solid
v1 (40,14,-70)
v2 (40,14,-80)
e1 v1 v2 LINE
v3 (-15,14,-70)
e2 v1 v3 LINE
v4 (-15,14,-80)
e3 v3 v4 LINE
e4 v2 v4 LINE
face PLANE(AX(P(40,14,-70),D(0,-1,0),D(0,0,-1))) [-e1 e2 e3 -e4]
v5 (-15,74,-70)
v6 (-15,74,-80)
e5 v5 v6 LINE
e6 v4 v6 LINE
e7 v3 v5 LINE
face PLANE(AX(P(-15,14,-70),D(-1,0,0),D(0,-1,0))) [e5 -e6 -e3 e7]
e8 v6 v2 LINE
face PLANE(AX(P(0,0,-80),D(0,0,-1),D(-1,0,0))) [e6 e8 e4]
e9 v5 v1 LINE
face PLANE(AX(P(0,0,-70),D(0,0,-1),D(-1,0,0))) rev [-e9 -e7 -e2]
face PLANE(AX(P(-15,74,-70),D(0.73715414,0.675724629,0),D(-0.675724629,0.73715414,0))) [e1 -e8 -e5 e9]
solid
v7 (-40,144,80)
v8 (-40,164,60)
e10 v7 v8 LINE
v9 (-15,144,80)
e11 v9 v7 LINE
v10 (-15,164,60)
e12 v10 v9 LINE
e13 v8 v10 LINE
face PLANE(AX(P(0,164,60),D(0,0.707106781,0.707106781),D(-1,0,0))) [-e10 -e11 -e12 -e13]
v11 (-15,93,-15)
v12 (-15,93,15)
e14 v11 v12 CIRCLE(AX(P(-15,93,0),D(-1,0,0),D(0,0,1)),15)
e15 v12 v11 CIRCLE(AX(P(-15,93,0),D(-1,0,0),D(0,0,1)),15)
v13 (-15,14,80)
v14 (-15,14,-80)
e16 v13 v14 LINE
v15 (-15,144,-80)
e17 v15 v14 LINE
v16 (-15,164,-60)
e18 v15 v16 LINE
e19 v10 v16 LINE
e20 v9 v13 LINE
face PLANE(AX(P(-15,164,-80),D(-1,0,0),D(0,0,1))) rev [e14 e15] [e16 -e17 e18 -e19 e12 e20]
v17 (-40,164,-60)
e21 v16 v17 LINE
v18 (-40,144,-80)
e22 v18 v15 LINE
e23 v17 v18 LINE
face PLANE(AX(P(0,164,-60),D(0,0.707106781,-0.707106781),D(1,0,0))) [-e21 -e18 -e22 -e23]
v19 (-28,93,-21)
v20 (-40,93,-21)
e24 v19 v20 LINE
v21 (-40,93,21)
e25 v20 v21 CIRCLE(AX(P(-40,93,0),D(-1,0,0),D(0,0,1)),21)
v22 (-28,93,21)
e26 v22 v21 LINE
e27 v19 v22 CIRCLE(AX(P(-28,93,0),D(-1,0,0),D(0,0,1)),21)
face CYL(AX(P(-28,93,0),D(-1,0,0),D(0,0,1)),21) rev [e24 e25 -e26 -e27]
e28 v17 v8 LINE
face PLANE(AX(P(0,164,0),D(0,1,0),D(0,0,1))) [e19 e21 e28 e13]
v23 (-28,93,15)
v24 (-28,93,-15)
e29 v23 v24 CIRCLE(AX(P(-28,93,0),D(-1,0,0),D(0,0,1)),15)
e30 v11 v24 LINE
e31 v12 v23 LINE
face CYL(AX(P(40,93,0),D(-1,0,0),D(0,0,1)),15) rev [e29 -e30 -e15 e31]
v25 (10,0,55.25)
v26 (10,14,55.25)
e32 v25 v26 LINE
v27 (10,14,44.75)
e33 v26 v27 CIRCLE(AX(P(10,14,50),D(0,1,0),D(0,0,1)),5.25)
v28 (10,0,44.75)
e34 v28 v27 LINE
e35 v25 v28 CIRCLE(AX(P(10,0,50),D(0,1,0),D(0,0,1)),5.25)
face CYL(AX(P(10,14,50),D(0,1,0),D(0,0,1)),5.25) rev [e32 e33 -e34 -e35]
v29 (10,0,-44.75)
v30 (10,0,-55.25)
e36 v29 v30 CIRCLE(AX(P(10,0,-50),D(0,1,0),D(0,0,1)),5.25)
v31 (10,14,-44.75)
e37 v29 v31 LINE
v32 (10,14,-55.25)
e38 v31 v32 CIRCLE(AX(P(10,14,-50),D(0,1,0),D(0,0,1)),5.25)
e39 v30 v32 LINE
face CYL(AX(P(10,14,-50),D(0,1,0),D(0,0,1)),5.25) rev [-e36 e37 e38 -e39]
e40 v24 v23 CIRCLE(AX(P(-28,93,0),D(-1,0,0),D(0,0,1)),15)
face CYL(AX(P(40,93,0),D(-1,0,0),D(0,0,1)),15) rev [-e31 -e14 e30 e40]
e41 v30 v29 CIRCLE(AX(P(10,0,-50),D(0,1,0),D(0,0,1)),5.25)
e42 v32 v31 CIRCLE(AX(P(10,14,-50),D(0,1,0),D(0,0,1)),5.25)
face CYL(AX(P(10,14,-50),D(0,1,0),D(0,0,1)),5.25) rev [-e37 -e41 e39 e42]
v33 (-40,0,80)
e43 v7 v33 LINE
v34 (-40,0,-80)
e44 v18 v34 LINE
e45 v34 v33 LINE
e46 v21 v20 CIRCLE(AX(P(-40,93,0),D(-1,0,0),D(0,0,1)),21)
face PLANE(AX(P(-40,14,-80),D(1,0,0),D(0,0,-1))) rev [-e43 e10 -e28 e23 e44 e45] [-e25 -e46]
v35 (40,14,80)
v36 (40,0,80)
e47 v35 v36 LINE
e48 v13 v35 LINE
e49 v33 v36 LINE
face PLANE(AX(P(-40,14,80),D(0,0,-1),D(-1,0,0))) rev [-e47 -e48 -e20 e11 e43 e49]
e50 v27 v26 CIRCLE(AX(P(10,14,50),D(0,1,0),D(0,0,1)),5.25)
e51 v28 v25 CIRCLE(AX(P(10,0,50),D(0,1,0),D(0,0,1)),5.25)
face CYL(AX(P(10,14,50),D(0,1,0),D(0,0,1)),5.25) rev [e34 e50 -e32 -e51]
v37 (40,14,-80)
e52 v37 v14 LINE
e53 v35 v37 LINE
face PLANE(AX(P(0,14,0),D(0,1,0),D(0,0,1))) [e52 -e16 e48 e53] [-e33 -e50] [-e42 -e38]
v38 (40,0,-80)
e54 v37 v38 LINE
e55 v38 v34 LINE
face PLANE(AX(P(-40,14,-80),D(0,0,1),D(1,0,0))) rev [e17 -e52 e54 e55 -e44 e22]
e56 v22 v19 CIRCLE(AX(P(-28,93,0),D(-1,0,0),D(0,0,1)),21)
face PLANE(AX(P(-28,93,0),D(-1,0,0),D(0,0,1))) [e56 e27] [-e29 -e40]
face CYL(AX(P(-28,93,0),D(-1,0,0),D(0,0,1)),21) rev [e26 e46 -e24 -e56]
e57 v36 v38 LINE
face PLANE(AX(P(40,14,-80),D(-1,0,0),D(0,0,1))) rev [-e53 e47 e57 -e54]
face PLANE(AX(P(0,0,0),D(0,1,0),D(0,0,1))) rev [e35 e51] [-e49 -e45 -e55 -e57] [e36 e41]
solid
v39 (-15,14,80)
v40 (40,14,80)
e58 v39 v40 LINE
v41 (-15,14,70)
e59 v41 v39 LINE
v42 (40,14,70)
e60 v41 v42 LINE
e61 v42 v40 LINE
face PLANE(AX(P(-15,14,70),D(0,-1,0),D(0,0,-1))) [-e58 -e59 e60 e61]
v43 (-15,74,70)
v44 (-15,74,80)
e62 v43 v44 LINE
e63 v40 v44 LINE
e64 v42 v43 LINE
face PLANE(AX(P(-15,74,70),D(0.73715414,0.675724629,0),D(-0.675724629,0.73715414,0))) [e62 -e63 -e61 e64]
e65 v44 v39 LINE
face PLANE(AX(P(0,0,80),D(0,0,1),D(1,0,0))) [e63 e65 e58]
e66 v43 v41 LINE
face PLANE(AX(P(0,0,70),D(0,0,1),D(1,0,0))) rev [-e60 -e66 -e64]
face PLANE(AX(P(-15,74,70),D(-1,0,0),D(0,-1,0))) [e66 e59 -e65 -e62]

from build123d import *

# Parameters (mm, degrees)
SKETCH_1_W                         = 80
SKETCH_1_H                         = 160
EXTRUDE_1_DEPTH                    = 14
SKETCH_2_W                         = 25
SKETCH_2_H                         = 160
EXTRUDE_2_DEPTH                    = 150
EXTRUDE_3_DEPTH                    = 10
EXTRUDE_4_DEPTH                    = 10
SKETCH_5_R                         = 21
CUT_EXTRUDE_1_DEPTH                = 12
SKETCH_6_R                         = 15
CUT_EXTRUDE_2_DEPTH                = 195.730583114
HOLE_WIZARD_10_5_10_5_1_AT_2_COUNT = 2
HOLE_WIZARD_10_5_10_5_1_AT_2_PITCH = 100
CHAMFER_1_SIZE                     = 20


with BuildPart() as part:
    # 草图1 → 凸台-拉伸1 (new body)
    with BuildSketch(Plane(origin=(0, 0, 0), x_dir=(1, 0, 0), z_dir=(0, 1, 0))):
        Rectangle(SKETCH_1_W, SKETCH_1_H)
    extrude(amount=EXTRUDE_1_DEPTH)

    # 草图2 → 凸台-拉伸2 (add)
    with BuildSketch(Plane(origin=(0, 14, 0), x_dir=(1, 0, 0), z_dir=(0, 1, 0))):
        with Locations((-27.5, 0)):
            Rectangle(SKETCH_2_W, SKETCH_2_H)
    extrude(amount=EXTRUDE_2_DEPTH)

    # 草图5 → 切除-拉伸1 (cut)
    with BuildSketch(Plane.ZY.offset(40)):
        with Locations((0, 93)):
            Circle(SKETCH_5_R)
    extrude(amount=-CUT_EXTRUDE_1_DEPTH, mode=Mode.SUBTRACT)

    # 草图6 → 切除-拉伸2 (cut, through all)
    with BuildSketch(Plane.ZY.offset(28)):
        with Locations((0, 93)):
            Circle(SKETCH_6_R)
    extrude(amount=-CUT_EXTRUDE_2_DEPTH, mode=Mode.SUBTRACT)

    # 草图9 → Ø10.5 (10.5) 直径孔1 (revolve, cut)
    with BuildSketch(Plane(origin=(10, 14, -50), x_dir=(0, 0, 1), z_dir=(1, 0, 0))):
        Polygon((0, 0), (0, 18.15451825), (5.25, 15), (5.25, 0), align=None)
    hole_wizard_10_5_10_5_1 = revolve(axis=Axis((10, 20.35, -50), (0, -1, 0)), mode=Mode.SUBTRACT)

    # Ø10.5 (10.5) 直径孔1 at 2: Ø10.5 (10.5) 直径孔1 ×2
    with Locations(*[(0, 0, i * HOLE_WIZARD_10_5_10_5_1_AT_2_PITCH) for i in range(1, HOLE_WIZARD_10_5_10_5_1_AT_2_COUNT)]):
        add(hole_wizard_10_5_10_5_1, mode=Mode.SUBTRACT)

    # 倒角1
    chamfer_1_edges = [part.edges().sort_by_distance(p)[0] for p in [
        (-27.5, 164, 80),
        (-27.5, 164, -80),
    ]]
    chamfer(chamfer_1_edges, length=CHAMFER_1_SIZE)


with BuildPart() as body_2:
    # 草图3 → 凸台-拉伸3 (new body)
    with BuildSketch(Plane.XY.offset(80)):
        Polygon((-15, 74), (40, 14), (-15, 14), align=None)
    extrude(amount=-EXTRUDE_3_DEPTH)


with BuildPart() as body_3:
    # 草图4 → 凸台-拉伸4 (new body)
    with BuildSketch(Plane(origin=(0, 0, -80), x_dir=(-1, 0, 0), z_dir=(0, 0, -1))):
        Polygon((15, 14), (15, 74), (-40, 14), align=None)
    extrude(amount=-EXTRUDE_4_DEPTH)


solid = Compound([part.part, body_2.part, body_3.part])
